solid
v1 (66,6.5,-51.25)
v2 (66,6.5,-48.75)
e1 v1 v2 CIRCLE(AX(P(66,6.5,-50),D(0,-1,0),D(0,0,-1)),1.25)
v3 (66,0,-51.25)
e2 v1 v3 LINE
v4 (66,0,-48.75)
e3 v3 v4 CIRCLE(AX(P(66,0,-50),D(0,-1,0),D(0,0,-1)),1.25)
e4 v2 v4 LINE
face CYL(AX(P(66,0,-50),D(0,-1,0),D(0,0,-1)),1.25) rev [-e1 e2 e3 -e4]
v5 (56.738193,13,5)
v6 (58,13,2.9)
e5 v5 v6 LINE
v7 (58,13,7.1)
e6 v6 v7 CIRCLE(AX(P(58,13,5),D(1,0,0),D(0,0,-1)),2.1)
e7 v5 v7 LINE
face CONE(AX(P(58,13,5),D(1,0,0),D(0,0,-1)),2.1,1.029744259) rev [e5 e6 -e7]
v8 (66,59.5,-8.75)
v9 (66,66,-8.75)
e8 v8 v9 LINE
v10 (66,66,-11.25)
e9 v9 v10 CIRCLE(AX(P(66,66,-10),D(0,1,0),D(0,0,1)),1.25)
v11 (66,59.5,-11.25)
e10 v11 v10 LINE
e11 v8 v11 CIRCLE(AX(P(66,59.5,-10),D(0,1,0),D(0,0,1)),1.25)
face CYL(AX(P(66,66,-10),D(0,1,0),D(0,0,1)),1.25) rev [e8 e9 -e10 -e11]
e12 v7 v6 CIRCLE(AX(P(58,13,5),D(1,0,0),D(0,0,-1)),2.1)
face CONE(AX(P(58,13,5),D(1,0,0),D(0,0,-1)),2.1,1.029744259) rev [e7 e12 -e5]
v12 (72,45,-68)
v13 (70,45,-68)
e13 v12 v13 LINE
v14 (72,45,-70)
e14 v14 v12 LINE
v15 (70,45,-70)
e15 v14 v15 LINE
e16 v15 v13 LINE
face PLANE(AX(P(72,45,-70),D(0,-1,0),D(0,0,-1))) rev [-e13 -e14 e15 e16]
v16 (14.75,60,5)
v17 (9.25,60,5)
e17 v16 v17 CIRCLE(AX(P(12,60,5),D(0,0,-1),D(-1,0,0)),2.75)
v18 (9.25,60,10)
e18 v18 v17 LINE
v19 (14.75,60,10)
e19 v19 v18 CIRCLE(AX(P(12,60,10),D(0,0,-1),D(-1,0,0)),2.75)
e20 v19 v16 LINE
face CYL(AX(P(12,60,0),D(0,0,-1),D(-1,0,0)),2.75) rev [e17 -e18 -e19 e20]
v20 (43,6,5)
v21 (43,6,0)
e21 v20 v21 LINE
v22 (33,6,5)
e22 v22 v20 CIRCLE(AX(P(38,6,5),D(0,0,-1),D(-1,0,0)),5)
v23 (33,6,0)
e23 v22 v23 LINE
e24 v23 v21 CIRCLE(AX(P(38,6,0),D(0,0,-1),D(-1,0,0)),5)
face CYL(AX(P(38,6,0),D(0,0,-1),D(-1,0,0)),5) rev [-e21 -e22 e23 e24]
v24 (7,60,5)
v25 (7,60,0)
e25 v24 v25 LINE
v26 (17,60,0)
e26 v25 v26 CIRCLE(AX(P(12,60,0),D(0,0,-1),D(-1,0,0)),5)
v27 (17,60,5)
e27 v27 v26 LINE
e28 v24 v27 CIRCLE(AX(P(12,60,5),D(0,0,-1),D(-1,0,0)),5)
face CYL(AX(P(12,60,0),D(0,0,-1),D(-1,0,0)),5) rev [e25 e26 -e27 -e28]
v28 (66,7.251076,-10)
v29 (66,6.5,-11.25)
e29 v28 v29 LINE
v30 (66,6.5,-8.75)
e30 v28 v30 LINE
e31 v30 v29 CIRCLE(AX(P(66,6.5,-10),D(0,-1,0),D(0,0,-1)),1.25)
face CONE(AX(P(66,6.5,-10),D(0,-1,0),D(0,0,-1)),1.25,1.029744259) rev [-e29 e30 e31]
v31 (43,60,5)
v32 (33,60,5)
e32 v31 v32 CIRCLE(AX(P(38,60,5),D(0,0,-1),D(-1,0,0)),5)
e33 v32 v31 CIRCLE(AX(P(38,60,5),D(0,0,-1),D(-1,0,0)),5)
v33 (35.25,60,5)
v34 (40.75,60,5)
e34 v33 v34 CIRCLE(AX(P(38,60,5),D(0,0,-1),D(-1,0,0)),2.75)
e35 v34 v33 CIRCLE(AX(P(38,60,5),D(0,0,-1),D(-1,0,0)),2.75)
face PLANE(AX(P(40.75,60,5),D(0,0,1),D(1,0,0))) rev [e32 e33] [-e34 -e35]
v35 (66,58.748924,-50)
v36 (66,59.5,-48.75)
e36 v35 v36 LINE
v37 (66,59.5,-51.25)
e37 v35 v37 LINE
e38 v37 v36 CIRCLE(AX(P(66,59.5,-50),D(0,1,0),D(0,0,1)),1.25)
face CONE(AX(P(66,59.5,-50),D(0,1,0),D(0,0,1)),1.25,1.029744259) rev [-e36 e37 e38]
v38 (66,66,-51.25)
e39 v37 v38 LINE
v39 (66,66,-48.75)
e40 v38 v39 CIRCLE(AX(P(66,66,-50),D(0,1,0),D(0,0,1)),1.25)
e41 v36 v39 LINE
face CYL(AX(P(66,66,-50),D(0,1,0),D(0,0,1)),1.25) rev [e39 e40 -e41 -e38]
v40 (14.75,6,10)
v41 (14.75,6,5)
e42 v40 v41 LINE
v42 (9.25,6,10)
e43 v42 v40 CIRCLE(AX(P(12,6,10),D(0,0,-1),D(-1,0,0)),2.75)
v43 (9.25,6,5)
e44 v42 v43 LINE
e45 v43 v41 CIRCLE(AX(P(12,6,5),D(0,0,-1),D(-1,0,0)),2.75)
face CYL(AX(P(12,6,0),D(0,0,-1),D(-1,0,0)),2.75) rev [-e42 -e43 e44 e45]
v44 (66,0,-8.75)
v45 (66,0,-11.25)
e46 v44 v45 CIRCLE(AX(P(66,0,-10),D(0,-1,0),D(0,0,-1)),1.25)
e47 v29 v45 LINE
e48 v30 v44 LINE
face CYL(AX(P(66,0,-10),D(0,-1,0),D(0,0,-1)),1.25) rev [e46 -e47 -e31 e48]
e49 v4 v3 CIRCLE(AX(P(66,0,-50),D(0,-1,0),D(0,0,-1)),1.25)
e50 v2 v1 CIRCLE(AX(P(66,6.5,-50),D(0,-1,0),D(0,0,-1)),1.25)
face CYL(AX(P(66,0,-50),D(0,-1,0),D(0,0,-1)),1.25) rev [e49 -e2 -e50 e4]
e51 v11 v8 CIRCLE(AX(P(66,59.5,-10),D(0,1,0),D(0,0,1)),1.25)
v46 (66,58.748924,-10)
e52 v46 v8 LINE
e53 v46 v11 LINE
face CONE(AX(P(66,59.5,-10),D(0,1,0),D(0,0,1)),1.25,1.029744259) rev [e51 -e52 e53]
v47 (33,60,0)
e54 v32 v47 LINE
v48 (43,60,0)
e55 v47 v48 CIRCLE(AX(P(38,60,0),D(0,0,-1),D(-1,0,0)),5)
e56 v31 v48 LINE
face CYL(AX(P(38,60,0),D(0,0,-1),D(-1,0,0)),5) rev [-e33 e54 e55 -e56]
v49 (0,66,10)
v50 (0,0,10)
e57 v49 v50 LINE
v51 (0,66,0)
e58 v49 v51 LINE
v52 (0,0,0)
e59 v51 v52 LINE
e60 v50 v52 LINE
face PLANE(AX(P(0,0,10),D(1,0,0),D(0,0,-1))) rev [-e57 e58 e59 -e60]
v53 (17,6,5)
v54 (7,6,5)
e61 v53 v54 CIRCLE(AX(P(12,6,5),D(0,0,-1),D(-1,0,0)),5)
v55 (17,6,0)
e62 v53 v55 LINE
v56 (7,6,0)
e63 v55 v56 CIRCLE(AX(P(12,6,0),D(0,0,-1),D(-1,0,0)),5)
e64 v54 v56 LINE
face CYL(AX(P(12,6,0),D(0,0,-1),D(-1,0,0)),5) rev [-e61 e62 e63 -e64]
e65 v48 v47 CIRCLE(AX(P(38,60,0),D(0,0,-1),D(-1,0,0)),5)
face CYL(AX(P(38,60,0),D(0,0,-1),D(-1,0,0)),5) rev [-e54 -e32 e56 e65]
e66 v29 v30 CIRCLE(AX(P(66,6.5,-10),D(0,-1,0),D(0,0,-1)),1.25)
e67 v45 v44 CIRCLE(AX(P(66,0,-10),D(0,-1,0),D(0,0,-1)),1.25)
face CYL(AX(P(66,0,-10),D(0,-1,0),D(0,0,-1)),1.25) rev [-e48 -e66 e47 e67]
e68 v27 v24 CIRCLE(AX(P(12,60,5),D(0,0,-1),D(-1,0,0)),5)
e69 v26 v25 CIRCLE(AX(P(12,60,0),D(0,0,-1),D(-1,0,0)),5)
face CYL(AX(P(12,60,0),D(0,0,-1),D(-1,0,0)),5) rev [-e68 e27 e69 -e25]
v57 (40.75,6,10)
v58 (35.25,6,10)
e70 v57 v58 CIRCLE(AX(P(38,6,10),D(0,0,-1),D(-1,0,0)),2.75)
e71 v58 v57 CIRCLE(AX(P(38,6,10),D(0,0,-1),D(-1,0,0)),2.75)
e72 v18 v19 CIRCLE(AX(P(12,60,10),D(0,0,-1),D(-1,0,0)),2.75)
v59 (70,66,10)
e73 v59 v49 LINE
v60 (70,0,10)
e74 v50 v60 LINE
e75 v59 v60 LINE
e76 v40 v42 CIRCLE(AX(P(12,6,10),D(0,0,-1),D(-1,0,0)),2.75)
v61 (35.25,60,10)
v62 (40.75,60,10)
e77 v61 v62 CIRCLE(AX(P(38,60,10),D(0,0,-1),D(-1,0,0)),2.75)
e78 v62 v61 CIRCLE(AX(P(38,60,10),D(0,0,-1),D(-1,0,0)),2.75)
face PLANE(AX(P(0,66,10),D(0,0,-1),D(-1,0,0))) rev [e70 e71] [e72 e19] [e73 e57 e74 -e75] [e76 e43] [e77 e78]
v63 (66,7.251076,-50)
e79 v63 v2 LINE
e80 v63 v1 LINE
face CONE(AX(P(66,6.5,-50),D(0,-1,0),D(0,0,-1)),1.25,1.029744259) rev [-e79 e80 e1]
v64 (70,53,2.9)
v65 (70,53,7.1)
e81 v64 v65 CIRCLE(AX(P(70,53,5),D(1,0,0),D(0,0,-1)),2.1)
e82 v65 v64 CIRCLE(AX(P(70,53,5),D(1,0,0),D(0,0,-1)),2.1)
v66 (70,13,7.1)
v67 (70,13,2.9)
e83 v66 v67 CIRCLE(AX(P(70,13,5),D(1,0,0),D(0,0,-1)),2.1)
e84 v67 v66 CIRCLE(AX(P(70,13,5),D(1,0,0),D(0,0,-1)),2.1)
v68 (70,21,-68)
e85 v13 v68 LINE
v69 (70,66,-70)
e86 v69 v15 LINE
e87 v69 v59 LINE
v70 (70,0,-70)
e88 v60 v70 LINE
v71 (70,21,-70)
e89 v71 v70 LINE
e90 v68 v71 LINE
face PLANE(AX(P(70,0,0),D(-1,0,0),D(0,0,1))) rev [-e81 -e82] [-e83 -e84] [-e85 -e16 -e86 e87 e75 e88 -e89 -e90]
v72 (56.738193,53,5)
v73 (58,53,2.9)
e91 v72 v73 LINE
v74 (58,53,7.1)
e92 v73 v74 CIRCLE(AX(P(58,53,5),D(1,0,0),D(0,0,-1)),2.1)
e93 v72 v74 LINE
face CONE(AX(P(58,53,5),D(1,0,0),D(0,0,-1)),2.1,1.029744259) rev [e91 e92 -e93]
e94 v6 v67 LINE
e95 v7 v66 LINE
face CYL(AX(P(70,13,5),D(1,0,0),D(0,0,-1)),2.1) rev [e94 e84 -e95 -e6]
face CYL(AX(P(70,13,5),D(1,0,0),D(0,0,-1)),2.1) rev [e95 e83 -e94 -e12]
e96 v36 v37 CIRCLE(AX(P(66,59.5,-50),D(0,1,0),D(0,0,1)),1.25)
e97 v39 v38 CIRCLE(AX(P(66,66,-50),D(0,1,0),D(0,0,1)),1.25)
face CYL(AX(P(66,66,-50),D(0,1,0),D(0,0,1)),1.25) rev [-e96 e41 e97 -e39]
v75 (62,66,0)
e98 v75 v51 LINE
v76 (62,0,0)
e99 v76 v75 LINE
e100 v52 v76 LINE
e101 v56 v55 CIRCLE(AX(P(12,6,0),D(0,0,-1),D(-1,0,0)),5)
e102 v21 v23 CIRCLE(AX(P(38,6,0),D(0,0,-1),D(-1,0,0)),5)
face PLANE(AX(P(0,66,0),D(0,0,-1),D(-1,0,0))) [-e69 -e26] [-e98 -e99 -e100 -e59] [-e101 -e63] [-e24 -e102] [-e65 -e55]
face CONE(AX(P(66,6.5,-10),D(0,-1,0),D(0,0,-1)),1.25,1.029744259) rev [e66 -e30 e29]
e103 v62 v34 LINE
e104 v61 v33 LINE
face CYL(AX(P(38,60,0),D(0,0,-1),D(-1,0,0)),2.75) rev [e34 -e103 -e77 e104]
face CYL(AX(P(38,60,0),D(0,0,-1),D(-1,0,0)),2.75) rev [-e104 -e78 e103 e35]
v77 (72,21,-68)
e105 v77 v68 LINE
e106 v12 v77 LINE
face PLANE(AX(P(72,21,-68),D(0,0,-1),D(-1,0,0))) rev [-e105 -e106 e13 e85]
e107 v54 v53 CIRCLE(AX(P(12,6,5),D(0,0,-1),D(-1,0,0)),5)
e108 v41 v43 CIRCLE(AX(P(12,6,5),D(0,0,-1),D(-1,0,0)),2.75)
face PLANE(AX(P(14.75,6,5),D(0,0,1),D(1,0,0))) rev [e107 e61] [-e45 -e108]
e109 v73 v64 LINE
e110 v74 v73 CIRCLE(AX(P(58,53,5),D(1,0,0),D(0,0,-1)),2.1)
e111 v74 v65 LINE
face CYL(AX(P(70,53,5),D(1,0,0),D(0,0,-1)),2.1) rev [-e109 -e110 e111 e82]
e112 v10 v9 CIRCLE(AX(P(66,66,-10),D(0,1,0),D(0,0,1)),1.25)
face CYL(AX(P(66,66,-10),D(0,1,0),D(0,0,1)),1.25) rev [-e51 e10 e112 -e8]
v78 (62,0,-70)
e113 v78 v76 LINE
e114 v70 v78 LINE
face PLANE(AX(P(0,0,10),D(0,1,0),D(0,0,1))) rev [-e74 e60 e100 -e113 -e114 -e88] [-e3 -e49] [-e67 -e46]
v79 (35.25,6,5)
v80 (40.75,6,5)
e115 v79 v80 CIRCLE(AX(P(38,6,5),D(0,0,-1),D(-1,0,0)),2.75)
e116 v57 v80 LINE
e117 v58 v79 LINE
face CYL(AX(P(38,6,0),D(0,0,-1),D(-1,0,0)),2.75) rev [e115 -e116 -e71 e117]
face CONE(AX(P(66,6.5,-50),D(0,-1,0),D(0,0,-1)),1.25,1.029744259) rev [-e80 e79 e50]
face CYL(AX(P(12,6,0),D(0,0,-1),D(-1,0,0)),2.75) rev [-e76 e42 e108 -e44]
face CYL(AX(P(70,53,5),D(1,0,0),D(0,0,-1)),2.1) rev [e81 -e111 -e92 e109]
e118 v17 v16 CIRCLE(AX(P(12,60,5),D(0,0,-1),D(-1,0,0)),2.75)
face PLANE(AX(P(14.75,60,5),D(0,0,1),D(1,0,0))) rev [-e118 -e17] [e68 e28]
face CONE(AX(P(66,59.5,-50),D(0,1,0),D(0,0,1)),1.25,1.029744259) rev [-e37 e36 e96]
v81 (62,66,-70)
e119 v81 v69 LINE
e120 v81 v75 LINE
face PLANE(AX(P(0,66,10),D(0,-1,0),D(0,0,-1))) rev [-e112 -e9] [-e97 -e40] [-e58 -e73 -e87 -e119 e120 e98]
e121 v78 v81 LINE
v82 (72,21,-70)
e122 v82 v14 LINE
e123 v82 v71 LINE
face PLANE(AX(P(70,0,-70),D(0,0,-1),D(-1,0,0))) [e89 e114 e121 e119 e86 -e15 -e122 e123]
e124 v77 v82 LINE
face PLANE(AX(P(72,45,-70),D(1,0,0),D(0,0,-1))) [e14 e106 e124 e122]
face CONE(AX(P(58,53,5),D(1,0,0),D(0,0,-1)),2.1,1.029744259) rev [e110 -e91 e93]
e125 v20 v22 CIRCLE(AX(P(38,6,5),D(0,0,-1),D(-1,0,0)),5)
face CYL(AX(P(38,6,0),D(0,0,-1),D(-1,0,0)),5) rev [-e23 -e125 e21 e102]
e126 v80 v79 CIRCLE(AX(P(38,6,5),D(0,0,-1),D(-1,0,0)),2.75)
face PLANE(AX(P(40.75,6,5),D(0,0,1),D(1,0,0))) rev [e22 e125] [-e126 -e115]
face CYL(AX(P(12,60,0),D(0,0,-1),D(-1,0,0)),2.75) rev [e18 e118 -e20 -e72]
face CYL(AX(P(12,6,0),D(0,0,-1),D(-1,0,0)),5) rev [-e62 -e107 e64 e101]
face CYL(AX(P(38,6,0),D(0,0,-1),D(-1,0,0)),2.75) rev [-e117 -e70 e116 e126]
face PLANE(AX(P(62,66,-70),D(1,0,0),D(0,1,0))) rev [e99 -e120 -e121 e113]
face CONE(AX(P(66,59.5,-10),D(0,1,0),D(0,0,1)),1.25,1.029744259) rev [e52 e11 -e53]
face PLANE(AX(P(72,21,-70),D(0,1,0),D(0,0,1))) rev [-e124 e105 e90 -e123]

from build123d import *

# Parameters (mm, degrees)
SKETCH_1_W                   = 50
SKETCH_1_H                   = 66
EXTRUDE_1_DEPTH              = 10
HOLE_WIZARD_M5_1_D           = 5.5
HOLE_WIZARD_M5_1_CBORE_D     = 10
HOLE_WIZARD_M5_1_CBORE_DEPTH = 5
SKETCH_4_W                   = 10
SKETCH_4_H                   = 66
EXTRUDE_2_DEPTH              = 20
M5X0_8_2_D                   = 4.2
M5X0_8_2_DEPTH               = 12
M5X0_8_2_TIP                 = 1.2618073
SKETCH_12_W                  = 8
SKETCH_12_H                  = 66
EXTRUDE_3_DEPTH              = 70
SKETCH_14_W                  = 2
SKETCH_14_H                  = 24
EXTRUDE_4_DEPTH              = 2
HOLE_WIZARD_M3_1_AT_2_COUNT  = 2
HOLE_WIZARD_M3_1_AT_2_PITCH  = 40


with BuildPart() as part:
    # 草图1 → 拉伸1 (new body)
    with BuildSketch(Plane.XY):
        with Locations((25, 33)):
            Rectangle(SKETCH_1_W, SKETCH_1_H)
    extrude(amount=EXTRUDE_1_DEPTH)

    # M5 凹头盖螺钉的柱形沉头孔1 (through all)
    with Locations(Plane(origin=(0, 0, 0), x_dir=(-1, 0, 0), z_dir=(0, 0, -1))):
        with Locations((-38, 6), (-38, 60), (-12, 60), (-12, 6)):
            CounterBoreHole(HOLE_WIZARD_M5_1_D / 2, HOLE_WIZARD_M5_1_CBORE_D / 2, HOLE_WIZARD_M5_1_CBORE_DEPTH)

    # 草图4 → 拉伸2 (add)
    with BuildSketch(Plane(origin=(50, 0, 0), x_dir=(0, 0, -1), z_dir=(1, 0, 0))):
        with Locations((-5, 33)):
            Rectangle(SKETCH_4_W, SKETCH_4_H)
    extrude(amount=EXTRUDE_2_DEPTH)

    # M5x0.8 螺纹孔2
    with Locations(Plane(origin=(70, 0, 0), x_dir=(0, 0, -1), z_dir=(1, 0, 0))):
        with Locations((-5, 53), (-5, 13)):
            Hole(M5X0_8_2_D / 2, depth=M5X0_8_2_DEPTH)
            with Locations((0, 0, -(M5X0_8_2_DEPTH + M5X0_8_2_TIP / 2))):  # 118° drill point
                Cone(0, M5X0_8_2_D / 2, M5X0_8_2_TIP, mode=Mode.SUBTRACT)

    # 草图12 → 拉伸3 (add)
    with BuildSketch(Plane(origin=(0, 0, 0), x_dir=(-1, 0, 0), z_dir=(0, 0, -1))):
        with Locations((-66, 33)):
            Rectangle(SKETCH_12_W, SKETCH_12_H)
    extrude(amount=EXTRUDE_3_DEPTH)

    # 草图14 → 拉伸4 (add)
    with BuildSketch(Plane(origin=(70, 0, 0), x_dir=(0, 0, -1), z_dir=(1, 0, 0))):
        with Locations((69, 33)):
            Rectangle(SKETCH_14_W, SKETCH_14_H)
    extrude(amount=EXTRUDE_4_DEPTH)

    # 草图15 → M3 螺纹孔1 (revolve, cut)
    with BuildSketch(Plane(origin=(66, 0, -10), x_dir=(0, 0, -1), z_dir=(1, 0, 0))):
        Polygon((0, 0), (0, 7.251075774), (1.25, 6.5), (1.25, 0), align=None)
    hole_wizard_m3_1 = revolve(axis=Axis((66, -6.35, -10), (0, 1, 0)), mode=Mode.SUBTRACT)

    # M3 螺纹孔1 at 2: M3 螺纹孔1 ×2
    with Locations(*[(0, 0, -i * HOLE_WIZARD_M3_1_AT_2_PITCH) for i in range(1, HOLE_WIZARD_M3_1_AT_2_COUNT)]):
        add(hole_wizard_m3_1, mode=Mode.SUBTRACT)

    # 镜向1: M3 螺纹孔1 across plane
    add(hole_wizard_m3_1.mirror(Plane(origin=(0, 33, 0), x_dir=(0, 0, 1), z_dir=(0, -1, 0))), mode=Mode.SUBTRACT)

    # 镜向1 copy 1 sketch → 镜向1 copy 1 (revolve, cut)
    with BuildSketch(Plane(origin=(66, 66, -50), x_dir=(0, 0, -1), z_dir=(1, 0, 0))):
        Polygon((0, 0), (0, -7.251075774), (1.25, -6.5), (1.25, 0), align=None)
    revolve(axis=Axis((66, 72.35, -50), (0, 1, 0)), mode=Mode.SUBTRACT)


solid = part.part
